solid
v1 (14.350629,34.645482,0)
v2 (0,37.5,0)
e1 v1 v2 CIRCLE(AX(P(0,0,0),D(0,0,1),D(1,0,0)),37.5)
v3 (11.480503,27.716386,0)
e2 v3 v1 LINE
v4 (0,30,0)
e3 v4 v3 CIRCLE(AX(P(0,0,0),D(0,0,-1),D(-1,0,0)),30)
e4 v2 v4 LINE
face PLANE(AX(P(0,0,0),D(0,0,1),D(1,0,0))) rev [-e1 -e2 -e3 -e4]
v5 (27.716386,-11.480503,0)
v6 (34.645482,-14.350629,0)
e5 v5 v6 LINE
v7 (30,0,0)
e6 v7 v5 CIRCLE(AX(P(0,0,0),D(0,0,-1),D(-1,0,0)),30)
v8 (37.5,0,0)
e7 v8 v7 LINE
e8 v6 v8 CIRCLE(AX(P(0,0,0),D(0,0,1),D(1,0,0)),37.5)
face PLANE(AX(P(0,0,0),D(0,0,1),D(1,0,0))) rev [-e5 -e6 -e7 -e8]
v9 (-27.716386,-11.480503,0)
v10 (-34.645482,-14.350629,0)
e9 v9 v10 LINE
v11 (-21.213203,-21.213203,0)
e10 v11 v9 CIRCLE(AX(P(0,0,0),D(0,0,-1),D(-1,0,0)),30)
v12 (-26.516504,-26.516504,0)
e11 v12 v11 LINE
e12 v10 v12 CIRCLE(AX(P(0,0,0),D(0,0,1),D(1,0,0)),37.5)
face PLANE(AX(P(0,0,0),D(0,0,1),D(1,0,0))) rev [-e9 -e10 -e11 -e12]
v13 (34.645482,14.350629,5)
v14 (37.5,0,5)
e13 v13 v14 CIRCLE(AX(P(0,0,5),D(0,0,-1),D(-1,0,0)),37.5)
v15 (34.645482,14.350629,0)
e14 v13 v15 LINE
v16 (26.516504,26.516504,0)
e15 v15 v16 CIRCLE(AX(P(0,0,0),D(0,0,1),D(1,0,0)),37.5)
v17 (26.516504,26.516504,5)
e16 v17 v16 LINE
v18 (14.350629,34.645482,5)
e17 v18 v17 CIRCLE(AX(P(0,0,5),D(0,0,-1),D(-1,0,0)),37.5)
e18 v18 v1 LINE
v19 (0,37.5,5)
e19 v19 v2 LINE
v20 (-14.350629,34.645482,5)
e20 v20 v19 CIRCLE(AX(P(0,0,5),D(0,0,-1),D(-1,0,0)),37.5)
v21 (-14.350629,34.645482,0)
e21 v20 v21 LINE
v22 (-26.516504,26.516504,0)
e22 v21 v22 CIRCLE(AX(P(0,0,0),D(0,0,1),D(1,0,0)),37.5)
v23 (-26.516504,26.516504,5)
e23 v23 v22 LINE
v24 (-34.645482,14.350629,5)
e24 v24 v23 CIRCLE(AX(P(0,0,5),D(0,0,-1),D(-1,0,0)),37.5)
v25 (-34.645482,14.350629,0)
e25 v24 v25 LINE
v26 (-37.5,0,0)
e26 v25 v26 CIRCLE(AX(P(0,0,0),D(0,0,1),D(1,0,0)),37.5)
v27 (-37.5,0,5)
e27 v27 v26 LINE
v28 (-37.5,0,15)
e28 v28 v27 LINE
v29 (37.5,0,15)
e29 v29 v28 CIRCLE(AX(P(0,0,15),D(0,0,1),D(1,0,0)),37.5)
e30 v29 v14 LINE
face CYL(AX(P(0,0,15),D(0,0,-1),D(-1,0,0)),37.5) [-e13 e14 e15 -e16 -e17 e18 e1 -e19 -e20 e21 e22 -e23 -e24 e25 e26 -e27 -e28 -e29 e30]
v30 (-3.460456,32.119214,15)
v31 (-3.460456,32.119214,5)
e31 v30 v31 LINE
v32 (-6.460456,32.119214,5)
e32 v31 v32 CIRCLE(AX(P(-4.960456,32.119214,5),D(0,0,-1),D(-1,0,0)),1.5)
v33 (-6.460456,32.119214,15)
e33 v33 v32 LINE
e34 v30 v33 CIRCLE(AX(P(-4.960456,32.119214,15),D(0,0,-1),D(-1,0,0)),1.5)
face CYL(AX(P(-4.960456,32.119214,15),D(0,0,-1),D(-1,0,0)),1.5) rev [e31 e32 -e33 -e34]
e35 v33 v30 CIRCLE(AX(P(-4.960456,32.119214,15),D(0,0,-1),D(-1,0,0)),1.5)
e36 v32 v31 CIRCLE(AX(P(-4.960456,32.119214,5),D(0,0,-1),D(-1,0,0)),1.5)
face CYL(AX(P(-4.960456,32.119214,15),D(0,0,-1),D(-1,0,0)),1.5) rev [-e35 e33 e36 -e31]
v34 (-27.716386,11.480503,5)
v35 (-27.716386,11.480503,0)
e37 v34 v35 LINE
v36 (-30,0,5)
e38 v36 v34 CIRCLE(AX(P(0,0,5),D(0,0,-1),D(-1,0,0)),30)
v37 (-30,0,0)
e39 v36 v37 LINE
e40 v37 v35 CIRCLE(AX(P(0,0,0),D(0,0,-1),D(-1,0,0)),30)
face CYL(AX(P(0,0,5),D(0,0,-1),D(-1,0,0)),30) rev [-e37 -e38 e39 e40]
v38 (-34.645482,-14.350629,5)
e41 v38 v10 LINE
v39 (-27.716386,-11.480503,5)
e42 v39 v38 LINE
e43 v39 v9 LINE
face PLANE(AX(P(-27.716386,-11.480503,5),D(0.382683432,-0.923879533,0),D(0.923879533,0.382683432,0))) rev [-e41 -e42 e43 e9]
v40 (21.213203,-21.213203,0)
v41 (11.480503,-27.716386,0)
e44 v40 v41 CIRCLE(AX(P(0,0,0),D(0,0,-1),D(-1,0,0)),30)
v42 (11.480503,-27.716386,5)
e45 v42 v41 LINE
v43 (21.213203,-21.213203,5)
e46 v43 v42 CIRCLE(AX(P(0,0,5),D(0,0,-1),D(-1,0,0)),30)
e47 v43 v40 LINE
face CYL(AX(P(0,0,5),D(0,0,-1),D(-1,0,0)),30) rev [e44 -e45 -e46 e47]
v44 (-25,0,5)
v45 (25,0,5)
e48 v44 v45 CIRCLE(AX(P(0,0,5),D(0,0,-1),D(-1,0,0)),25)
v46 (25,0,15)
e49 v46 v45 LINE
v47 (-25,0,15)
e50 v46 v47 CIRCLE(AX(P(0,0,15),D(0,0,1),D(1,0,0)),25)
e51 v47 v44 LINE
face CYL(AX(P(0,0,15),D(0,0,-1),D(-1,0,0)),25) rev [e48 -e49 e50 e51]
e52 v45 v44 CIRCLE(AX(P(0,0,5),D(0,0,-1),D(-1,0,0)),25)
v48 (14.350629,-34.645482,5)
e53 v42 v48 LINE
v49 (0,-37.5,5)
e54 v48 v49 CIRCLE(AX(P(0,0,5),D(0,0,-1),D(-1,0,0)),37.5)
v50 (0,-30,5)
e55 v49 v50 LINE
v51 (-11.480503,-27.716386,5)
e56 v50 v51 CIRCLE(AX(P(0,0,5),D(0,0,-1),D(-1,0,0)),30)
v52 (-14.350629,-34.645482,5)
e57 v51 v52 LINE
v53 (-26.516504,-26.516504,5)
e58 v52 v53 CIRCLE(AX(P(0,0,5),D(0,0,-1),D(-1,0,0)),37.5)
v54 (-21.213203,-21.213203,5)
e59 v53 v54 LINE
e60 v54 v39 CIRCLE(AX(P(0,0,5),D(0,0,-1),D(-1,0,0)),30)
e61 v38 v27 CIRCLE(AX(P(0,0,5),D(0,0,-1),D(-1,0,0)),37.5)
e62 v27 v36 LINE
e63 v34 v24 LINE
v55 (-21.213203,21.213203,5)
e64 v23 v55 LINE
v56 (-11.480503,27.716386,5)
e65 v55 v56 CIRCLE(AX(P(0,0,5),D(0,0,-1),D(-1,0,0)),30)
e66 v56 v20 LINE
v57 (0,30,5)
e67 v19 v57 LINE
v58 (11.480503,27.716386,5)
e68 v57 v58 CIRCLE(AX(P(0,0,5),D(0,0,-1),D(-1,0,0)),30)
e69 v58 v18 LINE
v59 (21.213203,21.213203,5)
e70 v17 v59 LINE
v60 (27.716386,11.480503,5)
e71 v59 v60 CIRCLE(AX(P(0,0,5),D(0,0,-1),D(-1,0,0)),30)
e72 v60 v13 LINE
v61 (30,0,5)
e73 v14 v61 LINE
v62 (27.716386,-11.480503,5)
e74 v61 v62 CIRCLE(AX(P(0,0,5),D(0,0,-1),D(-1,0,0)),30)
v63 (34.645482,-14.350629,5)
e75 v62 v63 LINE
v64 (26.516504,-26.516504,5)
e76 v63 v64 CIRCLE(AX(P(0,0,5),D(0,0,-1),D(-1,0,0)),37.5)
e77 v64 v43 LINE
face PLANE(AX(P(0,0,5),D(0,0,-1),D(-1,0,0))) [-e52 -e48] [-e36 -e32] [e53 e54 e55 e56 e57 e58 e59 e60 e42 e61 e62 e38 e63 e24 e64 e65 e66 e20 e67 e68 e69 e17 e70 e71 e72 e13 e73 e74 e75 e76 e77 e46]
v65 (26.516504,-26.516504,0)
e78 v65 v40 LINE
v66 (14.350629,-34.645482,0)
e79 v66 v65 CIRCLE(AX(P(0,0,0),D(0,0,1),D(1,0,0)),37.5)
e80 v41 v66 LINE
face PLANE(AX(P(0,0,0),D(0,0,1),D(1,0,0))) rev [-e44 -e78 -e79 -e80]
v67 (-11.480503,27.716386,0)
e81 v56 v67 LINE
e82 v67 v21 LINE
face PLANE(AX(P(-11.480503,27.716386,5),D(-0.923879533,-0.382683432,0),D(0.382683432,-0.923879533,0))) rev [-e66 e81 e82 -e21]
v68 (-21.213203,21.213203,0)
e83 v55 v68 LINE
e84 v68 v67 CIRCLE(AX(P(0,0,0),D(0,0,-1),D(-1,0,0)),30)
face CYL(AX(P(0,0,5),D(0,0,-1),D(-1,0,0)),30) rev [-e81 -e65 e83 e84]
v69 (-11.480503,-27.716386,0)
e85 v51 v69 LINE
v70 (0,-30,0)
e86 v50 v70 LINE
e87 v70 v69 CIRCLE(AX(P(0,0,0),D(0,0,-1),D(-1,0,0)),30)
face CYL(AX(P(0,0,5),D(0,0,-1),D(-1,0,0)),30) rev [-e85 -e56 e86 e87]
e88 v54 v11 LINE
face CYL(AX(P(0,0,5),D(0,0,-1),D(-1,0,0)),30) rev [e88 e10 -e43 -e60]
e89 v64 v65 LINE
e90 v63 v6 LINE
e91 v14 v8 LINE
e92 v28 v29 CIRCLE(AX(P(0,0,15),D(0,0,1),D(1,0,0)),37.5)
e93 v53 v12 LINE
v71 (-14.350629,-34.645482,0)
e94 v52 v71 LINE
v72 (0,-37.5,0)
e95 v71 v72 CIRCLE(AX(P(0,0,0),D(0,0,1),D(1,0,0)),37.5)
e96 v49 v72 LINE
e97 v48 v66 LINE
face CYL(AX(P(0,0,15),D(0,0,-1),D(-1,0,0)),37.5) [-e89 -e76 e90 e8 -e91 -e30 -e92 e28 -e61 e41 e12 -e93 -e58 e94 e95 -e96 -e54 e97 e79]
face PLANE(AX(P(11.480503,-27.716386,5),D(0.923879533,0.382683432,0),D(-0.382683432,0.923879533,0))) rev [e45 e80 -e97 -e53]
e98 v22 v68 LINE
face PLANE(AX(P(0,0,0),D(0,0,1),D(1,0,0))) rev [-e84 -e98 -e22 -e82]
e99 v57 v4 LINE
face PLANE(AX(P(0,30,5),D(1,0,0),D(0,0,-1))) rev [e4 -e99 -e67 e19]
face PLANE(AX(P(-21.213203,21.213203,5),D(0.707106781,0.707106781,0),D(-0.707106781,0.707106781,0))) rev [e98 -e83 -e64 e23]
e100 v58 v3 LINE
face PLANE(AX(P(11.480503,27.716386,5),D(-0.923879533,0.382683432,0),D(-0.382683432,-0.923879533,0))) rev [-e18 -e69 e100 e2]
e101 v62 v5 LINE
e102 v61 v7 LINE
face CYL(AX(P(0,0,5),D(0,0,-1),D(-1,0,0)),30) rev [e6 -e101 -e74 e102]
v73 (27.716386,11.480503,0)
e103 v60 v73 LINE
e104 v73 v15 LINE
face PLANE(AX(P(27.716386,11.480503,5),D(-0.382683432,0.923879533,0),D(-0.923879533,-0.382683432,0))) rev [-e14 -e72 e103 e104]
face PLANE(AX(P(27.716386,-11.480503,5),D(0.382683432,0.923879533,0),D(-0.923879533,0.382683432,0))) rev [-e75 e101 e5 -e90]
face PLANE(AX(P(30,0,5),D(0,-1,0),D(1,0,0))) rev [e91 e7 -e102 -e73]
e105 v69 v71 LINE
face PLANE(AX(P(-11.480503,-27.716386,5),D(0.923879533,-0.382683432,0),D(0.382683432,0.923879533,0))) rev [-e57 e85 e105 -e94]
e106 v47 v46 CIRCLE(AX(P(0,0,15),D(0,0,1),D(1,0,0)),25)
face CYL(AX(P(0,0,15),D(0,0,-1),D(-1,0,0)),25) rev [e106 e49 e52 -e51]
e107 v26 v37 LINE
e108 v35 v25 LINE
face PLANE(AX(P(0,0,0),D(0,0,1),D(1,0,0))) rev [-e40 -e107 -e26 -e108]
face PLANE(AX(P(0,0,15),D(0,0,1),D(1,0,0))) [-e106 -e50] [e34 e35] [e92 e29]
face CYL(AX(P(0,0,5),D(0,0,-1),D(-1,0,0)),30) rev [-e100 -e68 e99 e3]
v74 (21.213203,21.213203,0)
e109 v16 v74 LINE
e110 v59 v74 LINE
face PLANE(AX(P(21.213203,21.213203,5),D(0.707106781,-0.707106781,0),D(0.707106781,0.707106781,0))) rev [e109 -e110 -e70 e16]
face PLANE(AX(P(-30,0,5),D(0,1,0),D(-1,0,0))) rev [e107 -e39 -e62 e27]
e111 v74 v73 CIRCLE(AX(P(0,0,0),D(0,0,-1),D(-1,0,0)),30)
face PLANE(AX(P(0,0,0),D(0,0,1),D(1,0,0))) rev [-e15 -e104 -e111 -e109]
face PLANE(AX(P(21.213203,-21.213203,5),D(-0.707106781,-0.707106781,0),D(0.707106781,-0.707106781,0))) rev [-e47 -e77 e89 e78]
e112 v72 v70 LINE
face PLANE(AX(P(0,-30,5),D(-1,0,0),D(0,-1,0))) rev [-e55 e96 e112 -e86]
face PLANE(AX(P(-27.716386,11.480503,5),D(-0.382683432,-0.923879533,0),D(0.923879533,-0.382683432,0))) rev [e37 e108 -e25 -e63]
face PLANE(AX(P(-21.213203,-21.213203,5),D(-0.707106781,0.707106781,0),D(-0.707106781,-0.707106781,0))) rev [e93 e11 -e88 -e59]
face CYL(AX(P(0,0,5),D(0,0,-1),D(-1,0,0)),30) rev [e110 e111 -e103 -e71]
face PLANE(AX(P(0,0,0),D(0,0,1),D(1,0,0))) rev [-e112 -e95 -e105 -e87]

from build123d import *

# Parameters (mm, degrees)
SKETCH1_R           = 37.5
SKETCH1_R_2         = 25
BOSS_EXTRUDE1_DEPTH = 15
SKETCH2_R           = 30
CUT_EXTRUDE1_DEPTH  = 5
CUT_EXTRUDE2_DEPTH  = 5
SKETCH4_R           = 1.5
CUT_EXTRUDE3_DEPTH  = 10


with BuildPart() as part:
    # Sketch1 → Boss-Extrude1 (new body)
    with BuildSketch(Plane.XY):
        Circle(SKETCH1_R)
        Circle(SKETCH1_R_2, mode=Mode.SUBTRACT)
    extrude(amount=BOSS_EXTRUDE1_DEPTH)

    # Sketch2 → Cut-Extrude1 (cut)
    with BuildSketch(Plane(origin=(0, 0, 0), x_dir=(-1, 0, 0), z_dir=(0, 0, -1))):
        Circle(SKETCH2_R)
    extrude(amount=-CUT_EXTRUDE1_DEPTH, mode=Mode.SUBTRACT)

    # Sketch3 → Cut-Extrude2 (cut)
    with BuildSketch(Plane(origin=(0, 0, 0), x_dir=(-1, 0, 0), z_dir=(0, 0, -1))):
        with BuildLine():
            Line((0, 30), (0, 37.5))
            ThreePointArc((0, 37.5), (7.315887076, 36.779448015), (14.350628714, 34.645482469))
            Line((14.350628714, 34.645482469), (11.480502971, 27.716385975))
            ThreePointArc((11.480502971, 27.716385975), (5.85270966, 29.423558412), (0, 30))
        make_face()
        with BuildLine():
            Line((21.213203436, 21.213203436), (26.516504294, 26.516504294))
            ThreePointArc((26.516504294, 26.516504294), (31.180110461, 20.833883738), (34.645482469, 14.350628714))
            Line((34.645482469, 14.350628714), (27.716385975, 11.480502971))
            ThreePointArc((27.716385975, 11.480502971), (24.944088369, 16.667106991), (21.213203436, 21.213203436))
        make_face()
        with BuildLine():
            Line((30, 0), (37.5, 0))
            ThreePointArc((37.5, 0), (36.779448015, -7.315887076), (34.645482469, -14.350628714))
            Line((34.645482469, -14.350628714), (27.716385975, -11.480502971))
            ThreePointArc((27.716385975, -11.480502971), (29.423558412, -5.85270966), (30, 0))
        make_face()
        with BuildLine():
            Line((21.213203436, -21.213203436), (26.516504294, -26.516504294))
            ThreePointArc((26.516504294, -26.516504294), (20.833883738, -31.180110461), (14.350628714, -34.645482469))
            Line((14.350628714, -34.645482469), (11.480502971, -27.716385975))
            ThreePointArc((11.480502971, -27.716385975), (16.667106991, -24.944088369), (21.213203436, -21.213203436))
        make_face()
        with BuildLine():
            Line((0, -30), (0, -37.5))
            ThreePointArc((0, -37.5), (-7.315887076, -36.779448015), (-14.350628714, -34.645482469))
            Line((-14.350628714, -34.645482469), (-11.480502971, -27.716385975))
            ThreePointArc((-11.480502971, -27.716385975), (-5.85270966, -29.423558412), (0, -30))
        make_face()
        with BuildLine():
            Line((-21.213203436, -21.213203436), (-26.516504294, -26.516504294))
            ThreePointArc((-26.516504294, -26.516504294), (-31.180110461, -20.833883738), (-34.645482469, -14.350628714))
            Line((-34.645482469, -14.350628714), (-27.716385975, -11.480502971))
            ThreePointArc((-27.716385975, -11.480502971), (-24.944088369, -16.667106991), (-21.213203436, -21.213203436))
        make_face()
        with BuildLine():
            Line((-30, 0), (-37.5, 0))
            ThreePointArc((-37.5, 0), (-36.779448015, 7.315887076), (-34.645482469, 14.350628714))
            Line((-34.645482469, 14.350628714), (-27.716385975, 11.480502971))
            ThreePointArc((-27.716385975, 11.480502971), (-29.423558412, 5.85270966), (-30, 0))
        make_face()
        with BuildLine():
            Line((-21.213203436, 21.213203436), (-26.516504294, 26.516504294))
            ThreePointArc((-26.516504294, 26.516504294), (-20.833883738, 31.180110461), (-14.350628714, 34.645482469))
            Line((-14.350628714, 34.645482469), (-11.480502971, 27.716385975))
            ThreePointArc((-11.480502971, 27.716385975), (-16.667106991, 24.944088369), (-21.213203436, 21.213203436))
        make_face()
    extrude(amount=-CUT_EXTRUDE2_DEPTH, mode=Mode.SUBTRACT)

    # Sketch4 → Cut-Extrude3 (cut)
    with BuildSketch(Plane(origin=(0, 0, 5), x_dir=(-1, 0, 0), z_dir=(0, 0, -1))):
        with Locations((4.960455731, 32.119213548)):
            Circle(SKETCH4_R)
    extrude(amount=-CUT_EXTRUDE3_DEPTH, mode=Mode.SUBTRACT)


solid = part.part
